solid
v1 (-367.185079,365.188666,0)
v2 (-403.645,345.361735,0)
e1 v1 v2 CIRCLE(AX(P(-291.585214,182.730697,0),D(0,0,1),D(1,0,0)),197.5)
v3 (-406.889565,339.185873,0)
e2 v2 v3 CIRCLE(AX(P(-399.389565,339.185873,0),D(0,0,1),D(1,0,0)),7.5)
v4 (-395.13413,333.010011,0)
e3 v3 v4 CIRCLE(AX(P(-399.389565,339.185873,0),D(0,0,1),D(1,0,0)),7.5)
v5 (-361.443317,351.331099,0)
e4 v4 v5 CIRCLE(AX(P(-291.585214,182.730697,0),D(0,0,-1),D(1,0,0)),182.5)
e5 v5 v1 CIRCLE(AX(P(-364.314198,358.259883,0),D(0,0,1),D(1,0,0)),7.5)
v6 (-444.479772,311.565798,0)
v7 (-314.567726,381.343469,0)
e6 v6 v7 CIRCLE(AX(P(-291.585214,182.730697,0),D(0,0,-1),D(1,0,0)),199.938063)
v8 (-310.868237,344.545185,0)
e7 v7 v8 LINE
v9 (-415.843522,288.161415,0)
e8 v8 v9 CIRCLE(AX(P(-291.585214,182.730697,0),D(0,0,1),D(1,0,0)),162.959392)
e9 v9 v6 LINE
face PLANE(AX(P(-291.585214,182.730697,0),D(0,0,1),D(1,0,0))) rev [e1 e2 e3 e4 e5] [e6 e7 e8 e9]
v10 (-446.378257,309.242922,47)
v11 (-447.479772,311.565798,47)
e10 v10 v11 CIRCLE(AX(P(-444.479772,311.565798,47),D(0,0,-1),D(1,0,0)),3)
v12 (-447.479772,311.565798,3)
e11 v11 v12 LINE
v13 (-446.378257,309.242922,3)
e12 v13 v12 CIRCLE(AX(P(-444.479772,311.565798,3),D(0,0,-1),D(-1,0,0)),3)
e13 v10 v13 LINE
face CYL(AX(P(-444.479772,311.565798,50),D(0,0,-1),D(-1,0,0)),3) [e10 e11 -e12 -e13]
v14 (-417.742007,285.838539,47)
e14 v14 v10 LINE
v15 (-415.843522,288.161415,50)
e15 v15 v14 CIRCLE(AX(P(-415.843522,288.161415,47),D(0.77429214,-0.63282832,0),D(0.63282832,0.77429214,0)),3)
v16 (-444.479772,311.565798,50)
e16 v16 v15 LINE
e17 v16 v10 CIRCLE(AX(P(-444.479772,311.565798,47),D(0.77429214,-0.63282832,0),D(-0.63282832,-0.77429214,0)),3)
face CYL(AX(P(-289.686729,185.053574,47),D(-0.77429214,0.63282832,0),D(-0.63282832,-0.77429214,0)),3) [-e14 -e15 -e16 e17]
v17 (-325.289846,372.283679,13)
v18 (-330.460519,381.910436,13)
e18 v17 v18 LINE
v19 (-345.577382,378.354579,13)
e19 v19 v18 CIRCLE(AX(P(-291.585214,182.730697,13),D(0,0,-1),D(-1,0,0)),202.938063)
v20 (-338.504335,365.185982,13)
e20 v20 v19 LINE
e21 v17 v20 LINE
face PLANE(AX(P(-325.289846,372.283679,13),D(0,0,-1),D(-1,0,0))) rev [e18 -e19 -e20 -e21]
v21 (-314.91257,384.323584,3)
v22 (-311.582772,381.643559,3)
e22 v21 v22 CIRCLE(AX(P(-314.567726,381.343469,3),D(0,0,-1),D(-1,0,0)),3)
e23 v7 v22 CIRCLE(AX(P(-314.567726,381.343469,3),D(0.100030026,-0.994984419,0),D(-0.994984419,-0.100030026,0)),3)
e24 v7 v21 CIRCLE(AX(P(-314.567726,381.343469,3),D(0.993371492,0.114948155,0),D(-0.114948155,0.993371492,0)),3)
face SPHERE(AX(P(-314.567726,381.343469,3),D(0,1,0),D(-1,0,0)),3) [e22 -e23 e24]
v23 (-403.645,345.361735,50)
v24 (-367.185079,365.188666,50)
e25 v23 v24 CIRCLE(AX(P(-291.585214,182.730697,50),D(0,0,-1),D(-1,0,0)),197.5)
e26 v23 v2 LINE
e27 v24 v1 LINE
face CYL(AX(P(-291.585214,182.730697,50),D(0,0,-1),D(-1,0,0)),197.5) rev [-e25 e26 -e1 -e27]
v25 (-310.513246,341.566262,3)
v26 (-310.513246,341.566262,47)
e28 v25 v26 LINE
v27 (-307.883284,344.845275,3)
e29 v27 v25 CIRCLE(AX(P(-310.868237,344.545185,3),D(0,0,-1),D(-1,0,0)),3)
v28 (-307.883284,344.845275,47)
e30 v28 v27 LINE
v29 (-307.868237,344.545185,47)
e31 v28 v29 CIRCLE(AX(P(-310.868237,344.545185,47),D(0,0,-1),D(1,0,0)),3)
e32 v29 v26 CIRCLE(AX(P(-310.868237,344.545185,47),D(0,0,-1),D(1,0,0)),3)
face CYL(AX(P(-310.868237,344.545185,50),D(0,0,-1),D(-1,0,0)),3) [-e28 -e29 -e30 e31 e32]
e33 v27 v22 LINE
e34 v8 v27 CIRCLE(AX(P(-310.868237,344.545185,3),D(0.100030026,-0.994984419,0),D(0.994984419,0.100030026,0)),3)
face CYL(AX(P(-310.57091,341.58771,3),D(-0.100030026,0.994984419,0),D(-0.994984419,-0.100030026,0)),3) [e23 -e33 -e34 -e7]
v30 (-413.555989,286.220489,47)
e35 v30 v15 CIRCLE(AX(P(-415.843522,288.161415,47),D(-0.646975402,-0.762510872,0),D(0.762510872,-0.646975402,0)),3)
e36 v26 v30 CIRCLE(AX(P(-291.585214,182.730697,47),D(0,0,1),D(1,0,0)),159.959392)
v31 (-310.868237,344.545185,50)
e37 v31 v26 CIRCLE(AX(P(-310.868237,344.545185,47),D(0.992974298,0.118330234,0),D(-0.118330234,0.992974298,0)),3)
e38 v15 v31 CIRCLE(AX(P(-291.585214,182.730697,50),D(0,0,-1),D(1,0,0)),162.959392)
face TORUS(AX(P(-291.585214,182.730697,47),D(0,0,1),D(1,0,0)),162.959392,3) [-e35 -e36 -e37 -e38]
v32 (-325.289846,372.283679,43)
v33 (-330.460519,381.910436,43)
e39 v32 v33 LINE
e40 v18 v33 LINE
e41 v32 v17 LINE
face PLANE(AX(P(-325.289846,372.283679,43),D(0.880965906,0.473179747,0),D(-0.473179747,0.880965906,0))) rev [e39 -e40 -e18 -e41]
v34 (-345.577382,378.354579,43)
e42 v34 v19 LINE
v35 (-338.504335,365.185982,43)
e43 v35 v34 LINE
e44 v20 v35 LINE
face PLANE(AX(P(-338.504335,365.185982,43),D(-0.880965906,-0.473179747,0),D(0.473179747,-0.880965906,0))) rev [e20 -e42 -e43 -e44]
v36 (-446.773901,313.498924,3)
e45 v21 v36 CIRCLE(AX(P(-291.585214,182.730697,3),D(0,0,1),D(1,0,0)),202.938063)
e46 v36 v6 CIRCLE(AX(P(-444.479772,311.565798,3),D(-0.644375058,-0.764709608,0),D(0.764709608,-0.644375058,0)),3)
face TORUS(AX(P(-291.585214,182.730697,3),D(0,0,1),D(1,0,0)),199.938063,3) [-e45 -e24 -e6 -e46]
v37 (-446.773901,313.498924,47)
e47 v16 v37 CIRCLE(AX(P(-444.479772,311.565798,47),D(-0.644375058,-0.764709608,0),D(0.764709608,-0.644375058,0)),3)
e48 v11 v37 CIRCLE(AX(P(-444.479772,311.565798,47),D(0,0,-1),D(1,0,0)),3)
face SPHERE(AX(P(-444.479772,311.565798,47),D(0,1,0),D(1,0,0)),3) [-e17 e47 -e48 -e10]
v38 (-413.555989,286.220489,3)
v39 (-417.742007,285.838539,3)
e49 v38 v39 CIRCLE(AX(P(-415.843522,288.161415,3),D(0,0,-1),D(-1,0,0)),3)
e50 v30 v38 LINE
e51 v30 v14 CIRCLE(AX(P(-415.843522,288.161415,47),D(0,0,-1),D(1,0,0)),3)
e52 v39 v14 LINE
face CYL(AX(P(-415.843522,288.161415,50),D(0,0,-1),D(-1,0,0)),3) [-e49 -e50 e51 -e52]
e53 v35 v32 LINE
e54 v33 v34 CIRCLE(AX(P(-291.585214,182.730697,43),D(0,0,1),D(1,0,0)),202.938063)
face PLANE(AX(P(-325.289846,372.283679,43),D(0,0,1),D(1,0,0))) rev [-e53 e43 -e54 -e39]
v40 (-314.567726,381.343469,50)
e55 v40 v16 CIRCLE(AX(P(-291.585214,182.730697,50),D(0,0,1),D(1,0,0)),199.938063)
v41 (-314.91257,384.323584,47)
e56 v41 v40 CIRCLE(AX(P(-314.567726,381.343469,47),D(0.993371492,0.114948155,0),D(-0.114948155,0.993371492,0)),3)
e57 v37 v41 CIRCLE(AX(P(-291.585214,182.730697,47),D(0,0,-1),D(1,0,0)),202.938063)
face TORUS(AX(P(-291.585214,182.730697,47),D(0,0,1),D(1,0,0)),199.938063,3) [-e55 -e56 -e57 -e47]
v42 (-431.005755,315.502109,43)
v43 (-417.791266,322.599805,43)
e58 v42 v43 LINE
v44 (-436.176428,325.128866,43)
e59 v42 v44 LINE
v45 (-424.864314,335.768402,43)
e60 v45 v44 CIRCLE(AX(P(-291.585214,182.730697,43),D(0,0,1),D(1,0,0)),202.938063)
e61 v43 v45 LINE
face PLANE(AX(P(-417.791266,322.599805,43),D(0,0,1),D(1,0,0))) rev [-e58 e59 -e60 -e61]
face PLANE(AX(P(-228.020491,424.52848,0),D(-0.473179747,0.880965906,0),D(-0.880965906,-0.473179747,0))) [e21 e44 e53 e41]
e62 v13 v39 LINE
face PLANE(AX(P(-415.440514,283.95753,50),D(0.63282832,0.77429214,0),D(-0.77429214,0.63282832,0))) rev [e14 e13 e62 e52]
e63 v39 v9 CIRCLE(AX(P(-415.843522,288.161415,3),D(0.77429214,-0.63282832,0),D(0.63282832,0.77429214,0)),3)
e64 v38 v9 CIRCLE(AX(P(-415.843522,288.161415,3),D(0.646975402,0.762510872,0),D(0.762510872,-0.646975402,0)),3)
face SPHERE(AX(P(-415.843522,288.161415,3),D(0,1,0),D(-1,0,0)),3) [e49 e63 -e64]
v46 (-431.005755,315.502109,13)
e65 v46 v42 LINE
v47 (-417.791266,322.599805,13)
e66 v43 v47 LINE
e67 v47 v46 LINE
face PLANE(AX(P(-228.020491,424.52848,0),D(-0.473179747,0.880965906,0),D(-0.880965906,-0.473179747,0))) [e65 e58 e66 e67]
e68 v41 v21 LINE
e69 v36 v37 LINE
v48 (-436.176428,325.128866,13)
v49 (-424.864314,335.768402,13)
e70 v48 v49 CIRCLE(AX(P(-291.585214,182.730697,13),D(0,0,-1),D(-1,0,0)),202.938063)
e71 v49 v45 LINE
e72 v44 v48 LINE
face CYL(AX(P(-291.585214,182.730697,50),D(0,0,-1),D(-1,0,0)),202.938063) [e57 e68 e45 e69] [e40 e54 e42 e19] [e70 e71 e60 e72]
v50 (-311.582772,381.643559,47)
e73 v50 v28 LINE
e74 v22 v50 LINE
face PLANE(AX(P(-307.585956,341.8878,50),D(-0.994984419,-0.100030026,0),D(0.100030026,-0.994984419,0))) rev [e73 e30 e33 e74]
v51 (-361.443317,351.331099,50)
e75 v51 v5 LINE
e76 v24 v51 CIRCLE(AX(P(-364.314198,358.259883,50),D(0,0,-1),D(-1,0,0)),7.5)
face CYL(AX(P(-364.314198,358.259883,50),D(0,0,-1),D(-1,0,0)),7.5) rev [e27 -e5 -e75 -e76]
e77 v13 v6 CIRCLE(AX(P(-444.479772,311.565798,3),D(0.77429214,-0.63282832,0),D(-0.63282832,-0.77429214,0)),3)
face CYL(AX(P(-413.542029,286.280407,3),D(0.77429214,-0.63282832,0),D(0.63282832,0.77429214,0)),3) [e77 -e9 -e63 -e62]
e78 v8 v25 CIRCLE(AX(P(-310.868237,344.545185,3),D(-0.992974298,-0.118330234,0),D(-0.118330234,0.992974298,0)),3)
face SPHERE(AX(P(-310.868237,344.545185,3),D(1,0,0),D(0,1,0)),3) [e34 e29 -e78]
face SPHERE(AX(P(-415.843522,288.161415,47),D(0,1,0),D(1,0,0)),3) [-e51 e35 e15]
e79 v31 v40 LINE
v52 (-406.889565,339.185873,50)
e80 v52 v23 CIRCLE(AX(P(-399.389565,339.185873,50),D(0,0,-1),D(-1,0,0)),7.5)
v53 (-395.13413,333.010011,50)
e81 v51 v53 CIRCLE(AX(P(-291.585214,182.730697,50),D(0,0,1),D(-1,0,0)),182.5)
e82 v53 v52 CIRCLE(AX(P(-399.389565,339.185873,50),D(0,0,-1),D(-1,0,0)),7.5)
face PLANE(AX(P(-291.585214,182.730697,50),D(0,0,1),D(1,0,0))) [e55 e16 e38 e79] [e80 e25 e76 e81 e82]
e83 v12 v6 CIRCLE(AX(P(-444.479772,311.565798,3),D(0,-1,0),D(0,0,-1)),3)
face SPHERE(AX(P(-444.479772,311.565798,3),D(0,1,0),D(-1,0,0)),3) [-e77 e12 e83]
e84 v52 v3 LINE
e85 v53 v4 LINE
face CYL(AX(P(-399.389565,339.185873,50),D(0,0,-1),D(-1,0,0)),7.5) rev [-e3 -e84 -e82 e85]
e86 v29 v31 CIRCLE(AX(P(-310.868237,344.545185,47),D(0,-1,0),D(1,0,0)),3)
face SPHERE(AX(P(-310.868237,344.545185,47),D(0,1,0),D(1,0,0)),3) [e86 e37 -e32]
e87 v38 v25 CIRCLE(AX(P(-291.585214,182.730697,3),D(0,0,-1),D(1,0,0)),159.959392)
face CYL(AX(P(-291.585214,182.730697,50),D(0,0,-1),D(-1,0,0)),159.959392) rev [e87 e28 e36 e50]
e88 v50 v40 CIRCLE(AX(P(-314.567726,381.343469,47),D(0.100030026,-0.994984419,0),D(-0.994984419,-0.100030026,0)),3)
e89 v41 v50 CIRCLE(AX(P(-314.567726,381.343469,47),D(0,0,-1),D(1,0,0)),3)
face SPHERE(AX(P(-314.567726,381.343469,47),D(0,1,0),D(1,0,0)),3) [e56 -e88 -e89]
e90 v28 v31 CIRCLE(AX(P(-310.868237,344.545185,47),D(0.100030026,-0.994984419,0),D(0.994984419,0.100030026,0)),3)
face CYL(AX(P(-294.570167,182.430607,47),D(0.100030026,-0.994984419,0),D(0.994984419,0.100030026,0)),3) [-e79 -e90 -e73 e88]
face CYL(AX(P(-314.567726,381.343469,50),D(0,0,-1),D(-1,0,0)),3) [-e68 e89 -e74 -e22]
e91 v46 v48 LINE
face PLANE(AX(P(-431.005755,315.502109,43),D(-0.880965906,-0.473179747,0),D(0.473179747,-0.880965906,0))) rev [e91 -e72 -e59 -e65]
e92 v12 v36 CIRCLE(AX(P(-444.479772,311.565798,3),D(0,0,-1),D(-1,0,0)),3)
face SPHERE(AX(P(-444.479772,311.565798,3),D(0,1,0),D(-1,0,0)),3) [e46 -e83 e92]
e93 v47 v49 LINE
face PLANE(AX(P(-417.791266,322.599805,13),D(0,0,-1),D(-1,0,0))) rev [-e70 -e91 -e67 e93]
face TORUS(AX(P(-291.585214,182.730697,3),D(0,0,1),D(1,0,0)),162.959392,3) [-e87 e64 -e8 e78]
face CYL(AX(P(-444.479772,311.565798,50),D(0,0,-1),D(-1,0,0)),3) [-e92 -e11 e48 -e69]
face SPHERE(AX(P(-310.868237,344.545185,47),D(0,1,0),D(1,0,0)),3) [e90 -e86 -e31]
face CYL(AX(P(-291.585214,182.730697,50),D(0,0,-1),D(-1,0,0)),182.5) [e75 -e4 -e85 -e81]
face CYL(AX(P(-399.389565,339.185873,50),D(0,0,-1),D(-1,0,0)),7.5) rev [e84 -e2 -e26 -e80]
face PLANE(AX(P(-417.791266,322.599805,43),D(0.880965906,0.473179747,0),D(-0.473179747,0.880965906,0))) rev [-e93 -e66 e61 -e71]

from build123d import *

# Parameters (mm, degrees)
BOSS_EXTRUDE1_DEPTH     = 50
SKETCH2_W               = 15
SKETCH2_H               = 30
CUT_EXTRUDE1_DEPTH      = 20
CUT_EXTRUDE2_DEPTH      = 594.131240453
CUT_EXTRUDE2_DEPTH_BACK = 594.131240453
FILLET1_R               = 3


with BuildPart() as part:
    # Sketch1 → Boss-Extrude1 (new body)
    with BuildSketch(Plane.XY):
        with BuildLine():
            Line((-307.585956352, 341.88779966), (-311.885113994, 384.650908092))
            ThreePointArc((-311.885113994, 384.650908092), (-387.611395489, 361.512211901), (-448.718561356, 311.155650759))
            Line((-448.718561356, 311.155650759), (-415.440513877, 283.957530324))
            ThreePointArc((-415.440513877, 283.957530324), (-367.274758623, 323.649467677), (-307.585956352, 341.88779966))
        make_face()
    extrude(amount=BOSS_EXTRUDE1_DEPTH)

    # Sketch2 → Cut-Extrude1 (cut)
    with BuildSketch(Plane(origin=(-237.484086125, 442.147798063, 0), x_dir=(0.880965905900498, 0.47317974665122253, 0), z_dir=(-0.47317974665122253, 0.880965905900498, 0))):
        with Locations((-222.912167325, -28)):
            Rectangle(SKETCH2_W, SKETCH2_H)
        with Locations((-117.912167325, -28)):
            Rectangle(SKETCH2_W, SKETCH2_H)
    extrude(amount=-CUT_EXTRUDE1_DEPTH, mode=Mode.SUBTRACT)

    # Sketch3 → Cut-Extrude2 (cut, two sides: drawn at the far end of the back side and taken through both)
    with BuildSketch(Plane(origin=(0, 0, 0), x_dir=(-1, 0, 0), z_dir=(0, 0, -1)).offset(-CUT_EXTRUDE2_DEPTH_BACK)):
        with BuildLine():
            ThreePointArc((403.644999576, 345.361735137), (385.937282785, 356.235559249), (367.185078684, 365.188666312))
            ThreePointArc((367.185078684, 365.188666312), (357.385414117, 361.130763607), (361.443316822, 351.33109904))
            ThreePointArc((361.443316822, 351.33109904), (378.77130289, 343.057974791), (395.134129798, 333.010010739))
            ThreePointArc((395.134129798, 333.010010739), (405.565426886, 334.930438049), (403.644999576, 345.361735137))
        make_face()
    extrude(amount=CUT_EXTRUDE2_DEPTH + CUT_EXTRUDE2_DEPTH_BACK, mode=Mode.SUBTRACT)

    # Fillet1
    fillet1_edges = [part.edges().sort_by_distance(p)[0] for p in [
        (-387.611395489, 361.512211901, 50),
        (-432.079537616, 297.556590541, 50),
        (-367.274758623, 323.649467677, 50),
        (-432.079537616, 297.556590541, 0),
        (-387.611395489, 361.512211901, 0),
        (-309.735535173, 363.269353876, 0),
        (-367.274758623, 323.649467677, 0),
        (-415.440513877, 283.957530324, 25),
        (-448.718561356, 311.155650759, 25),
        (-311.885113994, 384.650908092, 25),
        (-307.585956352, 341.88779966, 25),
        (-309.735535173, 363.269353876, 50),
    ]]
    fillet(fillet1_edges, radius=FILLET1_R)


solid = part.part
